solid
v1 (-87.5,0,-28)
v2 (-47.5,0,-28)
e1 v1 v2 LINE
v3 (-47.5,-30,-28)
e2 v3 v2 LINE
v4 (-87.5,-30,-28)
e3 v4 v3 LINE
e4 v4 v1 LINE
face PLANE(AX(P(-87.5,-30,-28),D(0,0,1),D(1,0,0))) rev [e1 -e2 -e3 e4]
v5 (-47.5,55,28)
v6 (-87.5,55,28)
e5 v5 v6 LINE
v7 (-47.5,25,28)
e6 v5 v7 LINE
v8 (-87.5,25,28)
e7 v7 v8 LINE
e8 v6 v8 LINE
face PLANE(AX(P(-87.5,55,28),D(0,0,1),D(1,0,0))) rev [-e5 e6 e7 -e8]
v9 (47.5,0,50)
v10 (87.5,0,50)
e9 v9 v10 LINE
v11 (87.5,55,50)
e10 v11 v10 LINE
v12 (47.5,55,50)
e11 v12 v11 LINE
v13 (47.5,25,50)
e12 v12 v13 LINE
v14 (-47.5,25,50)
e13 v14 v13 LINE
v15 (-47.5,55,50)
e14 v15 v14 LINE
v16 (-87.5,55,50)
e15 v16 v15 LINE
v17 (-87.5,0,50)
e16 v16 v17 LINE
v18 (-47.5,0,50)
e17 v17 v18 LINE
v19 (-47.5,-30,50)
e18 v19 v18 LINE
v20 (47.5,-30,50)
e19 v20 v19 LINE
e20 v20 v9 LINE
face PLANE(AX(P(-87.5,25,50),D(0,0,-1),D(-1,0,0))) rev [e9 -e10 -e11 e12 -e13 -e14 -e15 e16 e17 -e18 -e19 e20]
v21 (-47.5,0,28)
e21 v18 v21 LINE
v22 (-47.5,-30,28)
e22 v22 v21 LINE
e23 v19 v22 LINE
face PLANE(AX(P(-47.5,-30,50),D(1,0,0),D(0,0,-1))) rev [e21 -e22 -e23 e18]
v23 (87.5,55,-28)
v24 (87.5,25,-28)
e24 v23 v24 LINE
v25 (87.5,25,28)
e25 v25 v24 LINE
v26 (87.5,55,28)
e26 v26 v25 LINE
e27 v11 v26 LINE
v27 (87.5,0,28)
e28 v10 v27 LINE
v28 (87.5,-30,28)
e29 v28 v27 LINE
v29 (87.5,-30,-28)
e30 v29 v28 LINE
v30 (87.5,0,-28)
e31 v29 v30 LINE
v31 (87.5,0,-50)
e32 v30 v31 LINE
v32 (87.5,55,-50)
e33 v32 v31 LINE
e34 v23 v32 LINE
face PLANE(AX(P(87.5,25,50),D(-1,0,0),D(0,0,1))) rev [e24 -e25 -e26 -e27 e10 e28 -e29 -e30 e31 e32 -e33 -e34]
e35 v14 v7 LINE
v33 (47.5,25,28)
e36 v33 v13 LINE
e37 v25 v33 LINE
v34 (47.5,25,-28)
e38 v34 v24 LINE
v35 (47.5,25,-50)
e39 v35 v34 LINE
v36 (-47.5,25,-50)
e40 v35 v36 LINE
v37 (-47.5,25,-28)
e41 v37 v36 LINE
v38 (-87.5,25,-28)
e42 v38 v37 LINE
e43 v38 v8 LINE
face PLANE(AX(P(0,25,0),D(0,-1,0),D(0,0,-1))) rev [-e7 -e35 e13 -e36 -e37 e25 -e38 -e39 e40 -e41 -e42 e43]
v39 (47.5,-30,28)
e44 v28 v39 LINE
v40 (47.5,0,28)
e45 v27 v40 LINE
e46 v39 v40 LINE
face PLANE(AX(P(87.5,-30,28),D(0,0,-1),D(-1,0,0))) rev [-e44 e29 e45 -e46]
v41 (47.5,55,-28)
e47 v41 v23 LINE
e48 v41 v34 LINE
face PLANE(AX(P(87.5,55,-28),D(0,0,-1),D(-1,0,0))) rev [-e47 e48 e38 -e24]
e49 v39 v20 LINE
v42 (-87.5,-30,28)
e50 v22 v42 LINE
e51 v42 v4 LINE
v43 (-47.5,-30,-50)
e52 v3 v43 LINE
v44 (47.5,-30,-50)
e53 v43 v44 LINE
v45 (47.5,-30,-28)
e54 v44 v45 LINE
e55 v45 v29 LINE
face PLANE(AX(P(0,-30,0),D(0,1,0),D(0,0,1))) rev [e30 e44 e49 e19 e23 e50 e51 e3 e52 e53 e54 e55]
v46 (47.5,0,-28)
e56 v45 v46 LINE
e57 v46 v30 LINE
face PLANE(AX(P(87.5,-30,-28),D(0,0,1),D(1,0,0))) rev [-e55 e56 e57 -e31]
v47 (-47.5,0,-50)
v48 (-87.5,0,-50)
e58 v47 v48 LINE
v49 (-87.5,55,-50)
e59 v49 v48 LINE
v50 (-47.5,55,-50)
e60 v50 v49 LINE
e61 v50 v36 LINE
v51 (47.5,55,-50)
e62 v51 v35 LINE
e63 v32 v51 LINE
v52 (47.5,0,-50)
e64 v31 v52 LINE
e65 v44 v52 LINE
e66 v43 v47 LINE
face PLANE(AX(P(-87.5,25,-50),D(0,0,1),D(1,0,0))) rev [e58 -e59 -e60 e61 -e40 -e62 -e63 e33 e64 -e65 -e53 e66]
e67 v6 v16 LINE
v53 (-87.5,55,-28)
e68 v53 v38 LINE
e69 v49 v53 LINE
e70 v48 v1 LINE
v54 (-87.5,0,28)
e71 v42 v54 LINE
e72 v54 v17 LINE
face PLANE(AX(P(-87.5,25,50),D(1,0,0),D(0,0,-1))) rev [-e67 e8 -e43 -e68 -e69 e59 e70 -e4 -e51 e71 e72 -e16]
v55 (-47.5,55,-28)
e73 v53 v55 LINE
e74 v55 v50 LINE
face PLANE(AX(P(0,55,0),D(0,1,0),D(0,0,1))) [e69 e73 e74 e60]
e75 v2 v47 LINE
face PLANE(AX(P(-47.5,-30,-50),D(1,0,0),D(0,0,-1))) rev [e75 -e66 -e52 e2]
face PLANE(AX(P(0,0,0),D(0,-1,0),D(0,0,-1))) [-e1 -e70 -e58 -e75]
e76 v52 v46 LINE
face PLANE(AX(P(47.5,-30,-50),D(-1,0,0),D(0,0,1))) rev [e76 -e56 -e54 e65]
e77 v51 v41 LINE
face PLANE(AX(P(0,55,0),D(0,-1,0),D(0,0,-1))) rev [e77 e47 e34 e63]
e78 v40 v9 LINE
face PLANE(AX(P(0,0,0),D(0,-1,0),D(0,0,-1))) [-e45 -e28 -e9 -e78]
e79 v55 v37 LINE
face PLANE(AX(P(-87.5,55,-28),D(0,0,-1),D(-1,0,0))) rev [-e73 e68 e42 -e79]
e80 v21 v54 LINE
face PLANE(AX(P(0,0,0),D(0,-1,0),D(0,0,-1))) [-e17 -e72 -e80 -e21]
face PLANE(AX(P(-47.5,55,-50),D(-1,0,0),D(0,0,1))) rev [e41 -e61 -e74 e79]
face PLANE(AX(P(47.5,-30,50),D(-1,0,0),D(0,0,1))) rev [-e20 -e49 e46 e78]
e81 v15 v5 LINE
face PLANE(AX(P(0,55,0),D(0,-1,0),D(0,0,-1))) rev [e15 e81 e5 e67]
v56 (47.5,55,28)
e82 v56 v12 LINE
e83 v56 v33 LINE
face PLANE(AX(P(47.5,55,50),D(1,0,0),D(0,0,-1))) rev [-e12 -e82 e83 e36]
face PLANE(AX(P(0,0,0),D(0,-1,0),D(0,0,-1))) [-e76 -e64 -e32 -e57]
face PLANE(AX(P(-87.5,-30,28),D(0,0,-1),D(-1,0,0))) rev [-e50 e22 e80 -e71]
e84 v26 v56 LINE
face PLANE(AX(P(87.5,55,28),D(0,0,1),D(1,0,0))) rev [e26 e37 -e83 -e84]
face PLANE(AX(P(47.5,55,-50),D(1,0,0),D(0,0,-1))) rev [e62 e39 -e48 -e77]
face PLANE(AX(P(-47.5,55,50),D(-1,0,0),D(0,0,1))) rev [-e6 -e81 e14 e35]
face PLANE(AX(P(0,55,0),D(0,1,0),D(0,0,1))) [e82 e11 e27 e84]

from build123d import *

# Parameters (mm, degrees)
BASE_PLATE_SKETCH_W         = 175
BASE_PLATE_SKETCH_H         = 100
BASE_PLATE_175X100X25_DEPTH = 25
TOP_BLOCKS_SKETCH_W         = 40
TOP_BLOCKS_SKETCH_H         = 22
TOP_BLOCKS_4X40X22_DEPTH    = 30
BOTTOM_PADS_DEPTH           = 30


with BuildPart() as part:
    # Base Plate Sketch → Base Plate 175x100x25 (new body)
    with BuildSketch(Plane(origin=(0, 0, 0), x_dir=(1, 0, 0), z_dir=(0, 1, 0))):
        Rectangle(BASE_PLATE_SKETCH_W, BASE_PLATE_SKETCH_H)
    extrude(amount=BASE_PLATE_175X100X25_DEPTH)

    # Top Blocks Sketch → Top Blocks 4x40x22 (add)
    with BuildSketch(Plane(origin=(0, 25, 0), x_dir=(1, 0, 0), z_dir=(0, 1, 0))):
        with Locations((-67.5, -39)):
            Rectangle(TOP_BLOCKS_SKETCH_W, TOP_BLOCKS_SKETCH_H)
        with Locations((-67.5, 39)):
            Rectangle(TOP_BLOCKS_SKETCH_W, TOP_BLOCKS_SKETCH_H)
        with Locations((67.5, 39)):
            Rectangle(TOP_BLOCKS_SKETCH_W, TOP_BLOCKS_SKETCH_H)
        with Locations((67.5, -39)):
            Rectangle(TOP_BLOCKS_SKETCH_W, TOP_BLOCKS_SKETCH_H)
    extrude(amount=TOP_BLOCKS_4X40X22_DEPTH)

    # Bottom Pads Sketch → Bottom Pads (add)
    with BuildSketch(Plane.XZ):
        Polygon((-47.5, 50), (47.5, 50), (47.5, 28), (87.5, 28), (87.5, -28), (47.5, -28), (47.5, -50), (-47.5, -50), (-47.5, -28), (-87.5, -28), (-87.5, 28), (-47.5, 28), align=None)
    extrude(amount=BOTTOM_PADS_DEPTH)


solid = part.part
